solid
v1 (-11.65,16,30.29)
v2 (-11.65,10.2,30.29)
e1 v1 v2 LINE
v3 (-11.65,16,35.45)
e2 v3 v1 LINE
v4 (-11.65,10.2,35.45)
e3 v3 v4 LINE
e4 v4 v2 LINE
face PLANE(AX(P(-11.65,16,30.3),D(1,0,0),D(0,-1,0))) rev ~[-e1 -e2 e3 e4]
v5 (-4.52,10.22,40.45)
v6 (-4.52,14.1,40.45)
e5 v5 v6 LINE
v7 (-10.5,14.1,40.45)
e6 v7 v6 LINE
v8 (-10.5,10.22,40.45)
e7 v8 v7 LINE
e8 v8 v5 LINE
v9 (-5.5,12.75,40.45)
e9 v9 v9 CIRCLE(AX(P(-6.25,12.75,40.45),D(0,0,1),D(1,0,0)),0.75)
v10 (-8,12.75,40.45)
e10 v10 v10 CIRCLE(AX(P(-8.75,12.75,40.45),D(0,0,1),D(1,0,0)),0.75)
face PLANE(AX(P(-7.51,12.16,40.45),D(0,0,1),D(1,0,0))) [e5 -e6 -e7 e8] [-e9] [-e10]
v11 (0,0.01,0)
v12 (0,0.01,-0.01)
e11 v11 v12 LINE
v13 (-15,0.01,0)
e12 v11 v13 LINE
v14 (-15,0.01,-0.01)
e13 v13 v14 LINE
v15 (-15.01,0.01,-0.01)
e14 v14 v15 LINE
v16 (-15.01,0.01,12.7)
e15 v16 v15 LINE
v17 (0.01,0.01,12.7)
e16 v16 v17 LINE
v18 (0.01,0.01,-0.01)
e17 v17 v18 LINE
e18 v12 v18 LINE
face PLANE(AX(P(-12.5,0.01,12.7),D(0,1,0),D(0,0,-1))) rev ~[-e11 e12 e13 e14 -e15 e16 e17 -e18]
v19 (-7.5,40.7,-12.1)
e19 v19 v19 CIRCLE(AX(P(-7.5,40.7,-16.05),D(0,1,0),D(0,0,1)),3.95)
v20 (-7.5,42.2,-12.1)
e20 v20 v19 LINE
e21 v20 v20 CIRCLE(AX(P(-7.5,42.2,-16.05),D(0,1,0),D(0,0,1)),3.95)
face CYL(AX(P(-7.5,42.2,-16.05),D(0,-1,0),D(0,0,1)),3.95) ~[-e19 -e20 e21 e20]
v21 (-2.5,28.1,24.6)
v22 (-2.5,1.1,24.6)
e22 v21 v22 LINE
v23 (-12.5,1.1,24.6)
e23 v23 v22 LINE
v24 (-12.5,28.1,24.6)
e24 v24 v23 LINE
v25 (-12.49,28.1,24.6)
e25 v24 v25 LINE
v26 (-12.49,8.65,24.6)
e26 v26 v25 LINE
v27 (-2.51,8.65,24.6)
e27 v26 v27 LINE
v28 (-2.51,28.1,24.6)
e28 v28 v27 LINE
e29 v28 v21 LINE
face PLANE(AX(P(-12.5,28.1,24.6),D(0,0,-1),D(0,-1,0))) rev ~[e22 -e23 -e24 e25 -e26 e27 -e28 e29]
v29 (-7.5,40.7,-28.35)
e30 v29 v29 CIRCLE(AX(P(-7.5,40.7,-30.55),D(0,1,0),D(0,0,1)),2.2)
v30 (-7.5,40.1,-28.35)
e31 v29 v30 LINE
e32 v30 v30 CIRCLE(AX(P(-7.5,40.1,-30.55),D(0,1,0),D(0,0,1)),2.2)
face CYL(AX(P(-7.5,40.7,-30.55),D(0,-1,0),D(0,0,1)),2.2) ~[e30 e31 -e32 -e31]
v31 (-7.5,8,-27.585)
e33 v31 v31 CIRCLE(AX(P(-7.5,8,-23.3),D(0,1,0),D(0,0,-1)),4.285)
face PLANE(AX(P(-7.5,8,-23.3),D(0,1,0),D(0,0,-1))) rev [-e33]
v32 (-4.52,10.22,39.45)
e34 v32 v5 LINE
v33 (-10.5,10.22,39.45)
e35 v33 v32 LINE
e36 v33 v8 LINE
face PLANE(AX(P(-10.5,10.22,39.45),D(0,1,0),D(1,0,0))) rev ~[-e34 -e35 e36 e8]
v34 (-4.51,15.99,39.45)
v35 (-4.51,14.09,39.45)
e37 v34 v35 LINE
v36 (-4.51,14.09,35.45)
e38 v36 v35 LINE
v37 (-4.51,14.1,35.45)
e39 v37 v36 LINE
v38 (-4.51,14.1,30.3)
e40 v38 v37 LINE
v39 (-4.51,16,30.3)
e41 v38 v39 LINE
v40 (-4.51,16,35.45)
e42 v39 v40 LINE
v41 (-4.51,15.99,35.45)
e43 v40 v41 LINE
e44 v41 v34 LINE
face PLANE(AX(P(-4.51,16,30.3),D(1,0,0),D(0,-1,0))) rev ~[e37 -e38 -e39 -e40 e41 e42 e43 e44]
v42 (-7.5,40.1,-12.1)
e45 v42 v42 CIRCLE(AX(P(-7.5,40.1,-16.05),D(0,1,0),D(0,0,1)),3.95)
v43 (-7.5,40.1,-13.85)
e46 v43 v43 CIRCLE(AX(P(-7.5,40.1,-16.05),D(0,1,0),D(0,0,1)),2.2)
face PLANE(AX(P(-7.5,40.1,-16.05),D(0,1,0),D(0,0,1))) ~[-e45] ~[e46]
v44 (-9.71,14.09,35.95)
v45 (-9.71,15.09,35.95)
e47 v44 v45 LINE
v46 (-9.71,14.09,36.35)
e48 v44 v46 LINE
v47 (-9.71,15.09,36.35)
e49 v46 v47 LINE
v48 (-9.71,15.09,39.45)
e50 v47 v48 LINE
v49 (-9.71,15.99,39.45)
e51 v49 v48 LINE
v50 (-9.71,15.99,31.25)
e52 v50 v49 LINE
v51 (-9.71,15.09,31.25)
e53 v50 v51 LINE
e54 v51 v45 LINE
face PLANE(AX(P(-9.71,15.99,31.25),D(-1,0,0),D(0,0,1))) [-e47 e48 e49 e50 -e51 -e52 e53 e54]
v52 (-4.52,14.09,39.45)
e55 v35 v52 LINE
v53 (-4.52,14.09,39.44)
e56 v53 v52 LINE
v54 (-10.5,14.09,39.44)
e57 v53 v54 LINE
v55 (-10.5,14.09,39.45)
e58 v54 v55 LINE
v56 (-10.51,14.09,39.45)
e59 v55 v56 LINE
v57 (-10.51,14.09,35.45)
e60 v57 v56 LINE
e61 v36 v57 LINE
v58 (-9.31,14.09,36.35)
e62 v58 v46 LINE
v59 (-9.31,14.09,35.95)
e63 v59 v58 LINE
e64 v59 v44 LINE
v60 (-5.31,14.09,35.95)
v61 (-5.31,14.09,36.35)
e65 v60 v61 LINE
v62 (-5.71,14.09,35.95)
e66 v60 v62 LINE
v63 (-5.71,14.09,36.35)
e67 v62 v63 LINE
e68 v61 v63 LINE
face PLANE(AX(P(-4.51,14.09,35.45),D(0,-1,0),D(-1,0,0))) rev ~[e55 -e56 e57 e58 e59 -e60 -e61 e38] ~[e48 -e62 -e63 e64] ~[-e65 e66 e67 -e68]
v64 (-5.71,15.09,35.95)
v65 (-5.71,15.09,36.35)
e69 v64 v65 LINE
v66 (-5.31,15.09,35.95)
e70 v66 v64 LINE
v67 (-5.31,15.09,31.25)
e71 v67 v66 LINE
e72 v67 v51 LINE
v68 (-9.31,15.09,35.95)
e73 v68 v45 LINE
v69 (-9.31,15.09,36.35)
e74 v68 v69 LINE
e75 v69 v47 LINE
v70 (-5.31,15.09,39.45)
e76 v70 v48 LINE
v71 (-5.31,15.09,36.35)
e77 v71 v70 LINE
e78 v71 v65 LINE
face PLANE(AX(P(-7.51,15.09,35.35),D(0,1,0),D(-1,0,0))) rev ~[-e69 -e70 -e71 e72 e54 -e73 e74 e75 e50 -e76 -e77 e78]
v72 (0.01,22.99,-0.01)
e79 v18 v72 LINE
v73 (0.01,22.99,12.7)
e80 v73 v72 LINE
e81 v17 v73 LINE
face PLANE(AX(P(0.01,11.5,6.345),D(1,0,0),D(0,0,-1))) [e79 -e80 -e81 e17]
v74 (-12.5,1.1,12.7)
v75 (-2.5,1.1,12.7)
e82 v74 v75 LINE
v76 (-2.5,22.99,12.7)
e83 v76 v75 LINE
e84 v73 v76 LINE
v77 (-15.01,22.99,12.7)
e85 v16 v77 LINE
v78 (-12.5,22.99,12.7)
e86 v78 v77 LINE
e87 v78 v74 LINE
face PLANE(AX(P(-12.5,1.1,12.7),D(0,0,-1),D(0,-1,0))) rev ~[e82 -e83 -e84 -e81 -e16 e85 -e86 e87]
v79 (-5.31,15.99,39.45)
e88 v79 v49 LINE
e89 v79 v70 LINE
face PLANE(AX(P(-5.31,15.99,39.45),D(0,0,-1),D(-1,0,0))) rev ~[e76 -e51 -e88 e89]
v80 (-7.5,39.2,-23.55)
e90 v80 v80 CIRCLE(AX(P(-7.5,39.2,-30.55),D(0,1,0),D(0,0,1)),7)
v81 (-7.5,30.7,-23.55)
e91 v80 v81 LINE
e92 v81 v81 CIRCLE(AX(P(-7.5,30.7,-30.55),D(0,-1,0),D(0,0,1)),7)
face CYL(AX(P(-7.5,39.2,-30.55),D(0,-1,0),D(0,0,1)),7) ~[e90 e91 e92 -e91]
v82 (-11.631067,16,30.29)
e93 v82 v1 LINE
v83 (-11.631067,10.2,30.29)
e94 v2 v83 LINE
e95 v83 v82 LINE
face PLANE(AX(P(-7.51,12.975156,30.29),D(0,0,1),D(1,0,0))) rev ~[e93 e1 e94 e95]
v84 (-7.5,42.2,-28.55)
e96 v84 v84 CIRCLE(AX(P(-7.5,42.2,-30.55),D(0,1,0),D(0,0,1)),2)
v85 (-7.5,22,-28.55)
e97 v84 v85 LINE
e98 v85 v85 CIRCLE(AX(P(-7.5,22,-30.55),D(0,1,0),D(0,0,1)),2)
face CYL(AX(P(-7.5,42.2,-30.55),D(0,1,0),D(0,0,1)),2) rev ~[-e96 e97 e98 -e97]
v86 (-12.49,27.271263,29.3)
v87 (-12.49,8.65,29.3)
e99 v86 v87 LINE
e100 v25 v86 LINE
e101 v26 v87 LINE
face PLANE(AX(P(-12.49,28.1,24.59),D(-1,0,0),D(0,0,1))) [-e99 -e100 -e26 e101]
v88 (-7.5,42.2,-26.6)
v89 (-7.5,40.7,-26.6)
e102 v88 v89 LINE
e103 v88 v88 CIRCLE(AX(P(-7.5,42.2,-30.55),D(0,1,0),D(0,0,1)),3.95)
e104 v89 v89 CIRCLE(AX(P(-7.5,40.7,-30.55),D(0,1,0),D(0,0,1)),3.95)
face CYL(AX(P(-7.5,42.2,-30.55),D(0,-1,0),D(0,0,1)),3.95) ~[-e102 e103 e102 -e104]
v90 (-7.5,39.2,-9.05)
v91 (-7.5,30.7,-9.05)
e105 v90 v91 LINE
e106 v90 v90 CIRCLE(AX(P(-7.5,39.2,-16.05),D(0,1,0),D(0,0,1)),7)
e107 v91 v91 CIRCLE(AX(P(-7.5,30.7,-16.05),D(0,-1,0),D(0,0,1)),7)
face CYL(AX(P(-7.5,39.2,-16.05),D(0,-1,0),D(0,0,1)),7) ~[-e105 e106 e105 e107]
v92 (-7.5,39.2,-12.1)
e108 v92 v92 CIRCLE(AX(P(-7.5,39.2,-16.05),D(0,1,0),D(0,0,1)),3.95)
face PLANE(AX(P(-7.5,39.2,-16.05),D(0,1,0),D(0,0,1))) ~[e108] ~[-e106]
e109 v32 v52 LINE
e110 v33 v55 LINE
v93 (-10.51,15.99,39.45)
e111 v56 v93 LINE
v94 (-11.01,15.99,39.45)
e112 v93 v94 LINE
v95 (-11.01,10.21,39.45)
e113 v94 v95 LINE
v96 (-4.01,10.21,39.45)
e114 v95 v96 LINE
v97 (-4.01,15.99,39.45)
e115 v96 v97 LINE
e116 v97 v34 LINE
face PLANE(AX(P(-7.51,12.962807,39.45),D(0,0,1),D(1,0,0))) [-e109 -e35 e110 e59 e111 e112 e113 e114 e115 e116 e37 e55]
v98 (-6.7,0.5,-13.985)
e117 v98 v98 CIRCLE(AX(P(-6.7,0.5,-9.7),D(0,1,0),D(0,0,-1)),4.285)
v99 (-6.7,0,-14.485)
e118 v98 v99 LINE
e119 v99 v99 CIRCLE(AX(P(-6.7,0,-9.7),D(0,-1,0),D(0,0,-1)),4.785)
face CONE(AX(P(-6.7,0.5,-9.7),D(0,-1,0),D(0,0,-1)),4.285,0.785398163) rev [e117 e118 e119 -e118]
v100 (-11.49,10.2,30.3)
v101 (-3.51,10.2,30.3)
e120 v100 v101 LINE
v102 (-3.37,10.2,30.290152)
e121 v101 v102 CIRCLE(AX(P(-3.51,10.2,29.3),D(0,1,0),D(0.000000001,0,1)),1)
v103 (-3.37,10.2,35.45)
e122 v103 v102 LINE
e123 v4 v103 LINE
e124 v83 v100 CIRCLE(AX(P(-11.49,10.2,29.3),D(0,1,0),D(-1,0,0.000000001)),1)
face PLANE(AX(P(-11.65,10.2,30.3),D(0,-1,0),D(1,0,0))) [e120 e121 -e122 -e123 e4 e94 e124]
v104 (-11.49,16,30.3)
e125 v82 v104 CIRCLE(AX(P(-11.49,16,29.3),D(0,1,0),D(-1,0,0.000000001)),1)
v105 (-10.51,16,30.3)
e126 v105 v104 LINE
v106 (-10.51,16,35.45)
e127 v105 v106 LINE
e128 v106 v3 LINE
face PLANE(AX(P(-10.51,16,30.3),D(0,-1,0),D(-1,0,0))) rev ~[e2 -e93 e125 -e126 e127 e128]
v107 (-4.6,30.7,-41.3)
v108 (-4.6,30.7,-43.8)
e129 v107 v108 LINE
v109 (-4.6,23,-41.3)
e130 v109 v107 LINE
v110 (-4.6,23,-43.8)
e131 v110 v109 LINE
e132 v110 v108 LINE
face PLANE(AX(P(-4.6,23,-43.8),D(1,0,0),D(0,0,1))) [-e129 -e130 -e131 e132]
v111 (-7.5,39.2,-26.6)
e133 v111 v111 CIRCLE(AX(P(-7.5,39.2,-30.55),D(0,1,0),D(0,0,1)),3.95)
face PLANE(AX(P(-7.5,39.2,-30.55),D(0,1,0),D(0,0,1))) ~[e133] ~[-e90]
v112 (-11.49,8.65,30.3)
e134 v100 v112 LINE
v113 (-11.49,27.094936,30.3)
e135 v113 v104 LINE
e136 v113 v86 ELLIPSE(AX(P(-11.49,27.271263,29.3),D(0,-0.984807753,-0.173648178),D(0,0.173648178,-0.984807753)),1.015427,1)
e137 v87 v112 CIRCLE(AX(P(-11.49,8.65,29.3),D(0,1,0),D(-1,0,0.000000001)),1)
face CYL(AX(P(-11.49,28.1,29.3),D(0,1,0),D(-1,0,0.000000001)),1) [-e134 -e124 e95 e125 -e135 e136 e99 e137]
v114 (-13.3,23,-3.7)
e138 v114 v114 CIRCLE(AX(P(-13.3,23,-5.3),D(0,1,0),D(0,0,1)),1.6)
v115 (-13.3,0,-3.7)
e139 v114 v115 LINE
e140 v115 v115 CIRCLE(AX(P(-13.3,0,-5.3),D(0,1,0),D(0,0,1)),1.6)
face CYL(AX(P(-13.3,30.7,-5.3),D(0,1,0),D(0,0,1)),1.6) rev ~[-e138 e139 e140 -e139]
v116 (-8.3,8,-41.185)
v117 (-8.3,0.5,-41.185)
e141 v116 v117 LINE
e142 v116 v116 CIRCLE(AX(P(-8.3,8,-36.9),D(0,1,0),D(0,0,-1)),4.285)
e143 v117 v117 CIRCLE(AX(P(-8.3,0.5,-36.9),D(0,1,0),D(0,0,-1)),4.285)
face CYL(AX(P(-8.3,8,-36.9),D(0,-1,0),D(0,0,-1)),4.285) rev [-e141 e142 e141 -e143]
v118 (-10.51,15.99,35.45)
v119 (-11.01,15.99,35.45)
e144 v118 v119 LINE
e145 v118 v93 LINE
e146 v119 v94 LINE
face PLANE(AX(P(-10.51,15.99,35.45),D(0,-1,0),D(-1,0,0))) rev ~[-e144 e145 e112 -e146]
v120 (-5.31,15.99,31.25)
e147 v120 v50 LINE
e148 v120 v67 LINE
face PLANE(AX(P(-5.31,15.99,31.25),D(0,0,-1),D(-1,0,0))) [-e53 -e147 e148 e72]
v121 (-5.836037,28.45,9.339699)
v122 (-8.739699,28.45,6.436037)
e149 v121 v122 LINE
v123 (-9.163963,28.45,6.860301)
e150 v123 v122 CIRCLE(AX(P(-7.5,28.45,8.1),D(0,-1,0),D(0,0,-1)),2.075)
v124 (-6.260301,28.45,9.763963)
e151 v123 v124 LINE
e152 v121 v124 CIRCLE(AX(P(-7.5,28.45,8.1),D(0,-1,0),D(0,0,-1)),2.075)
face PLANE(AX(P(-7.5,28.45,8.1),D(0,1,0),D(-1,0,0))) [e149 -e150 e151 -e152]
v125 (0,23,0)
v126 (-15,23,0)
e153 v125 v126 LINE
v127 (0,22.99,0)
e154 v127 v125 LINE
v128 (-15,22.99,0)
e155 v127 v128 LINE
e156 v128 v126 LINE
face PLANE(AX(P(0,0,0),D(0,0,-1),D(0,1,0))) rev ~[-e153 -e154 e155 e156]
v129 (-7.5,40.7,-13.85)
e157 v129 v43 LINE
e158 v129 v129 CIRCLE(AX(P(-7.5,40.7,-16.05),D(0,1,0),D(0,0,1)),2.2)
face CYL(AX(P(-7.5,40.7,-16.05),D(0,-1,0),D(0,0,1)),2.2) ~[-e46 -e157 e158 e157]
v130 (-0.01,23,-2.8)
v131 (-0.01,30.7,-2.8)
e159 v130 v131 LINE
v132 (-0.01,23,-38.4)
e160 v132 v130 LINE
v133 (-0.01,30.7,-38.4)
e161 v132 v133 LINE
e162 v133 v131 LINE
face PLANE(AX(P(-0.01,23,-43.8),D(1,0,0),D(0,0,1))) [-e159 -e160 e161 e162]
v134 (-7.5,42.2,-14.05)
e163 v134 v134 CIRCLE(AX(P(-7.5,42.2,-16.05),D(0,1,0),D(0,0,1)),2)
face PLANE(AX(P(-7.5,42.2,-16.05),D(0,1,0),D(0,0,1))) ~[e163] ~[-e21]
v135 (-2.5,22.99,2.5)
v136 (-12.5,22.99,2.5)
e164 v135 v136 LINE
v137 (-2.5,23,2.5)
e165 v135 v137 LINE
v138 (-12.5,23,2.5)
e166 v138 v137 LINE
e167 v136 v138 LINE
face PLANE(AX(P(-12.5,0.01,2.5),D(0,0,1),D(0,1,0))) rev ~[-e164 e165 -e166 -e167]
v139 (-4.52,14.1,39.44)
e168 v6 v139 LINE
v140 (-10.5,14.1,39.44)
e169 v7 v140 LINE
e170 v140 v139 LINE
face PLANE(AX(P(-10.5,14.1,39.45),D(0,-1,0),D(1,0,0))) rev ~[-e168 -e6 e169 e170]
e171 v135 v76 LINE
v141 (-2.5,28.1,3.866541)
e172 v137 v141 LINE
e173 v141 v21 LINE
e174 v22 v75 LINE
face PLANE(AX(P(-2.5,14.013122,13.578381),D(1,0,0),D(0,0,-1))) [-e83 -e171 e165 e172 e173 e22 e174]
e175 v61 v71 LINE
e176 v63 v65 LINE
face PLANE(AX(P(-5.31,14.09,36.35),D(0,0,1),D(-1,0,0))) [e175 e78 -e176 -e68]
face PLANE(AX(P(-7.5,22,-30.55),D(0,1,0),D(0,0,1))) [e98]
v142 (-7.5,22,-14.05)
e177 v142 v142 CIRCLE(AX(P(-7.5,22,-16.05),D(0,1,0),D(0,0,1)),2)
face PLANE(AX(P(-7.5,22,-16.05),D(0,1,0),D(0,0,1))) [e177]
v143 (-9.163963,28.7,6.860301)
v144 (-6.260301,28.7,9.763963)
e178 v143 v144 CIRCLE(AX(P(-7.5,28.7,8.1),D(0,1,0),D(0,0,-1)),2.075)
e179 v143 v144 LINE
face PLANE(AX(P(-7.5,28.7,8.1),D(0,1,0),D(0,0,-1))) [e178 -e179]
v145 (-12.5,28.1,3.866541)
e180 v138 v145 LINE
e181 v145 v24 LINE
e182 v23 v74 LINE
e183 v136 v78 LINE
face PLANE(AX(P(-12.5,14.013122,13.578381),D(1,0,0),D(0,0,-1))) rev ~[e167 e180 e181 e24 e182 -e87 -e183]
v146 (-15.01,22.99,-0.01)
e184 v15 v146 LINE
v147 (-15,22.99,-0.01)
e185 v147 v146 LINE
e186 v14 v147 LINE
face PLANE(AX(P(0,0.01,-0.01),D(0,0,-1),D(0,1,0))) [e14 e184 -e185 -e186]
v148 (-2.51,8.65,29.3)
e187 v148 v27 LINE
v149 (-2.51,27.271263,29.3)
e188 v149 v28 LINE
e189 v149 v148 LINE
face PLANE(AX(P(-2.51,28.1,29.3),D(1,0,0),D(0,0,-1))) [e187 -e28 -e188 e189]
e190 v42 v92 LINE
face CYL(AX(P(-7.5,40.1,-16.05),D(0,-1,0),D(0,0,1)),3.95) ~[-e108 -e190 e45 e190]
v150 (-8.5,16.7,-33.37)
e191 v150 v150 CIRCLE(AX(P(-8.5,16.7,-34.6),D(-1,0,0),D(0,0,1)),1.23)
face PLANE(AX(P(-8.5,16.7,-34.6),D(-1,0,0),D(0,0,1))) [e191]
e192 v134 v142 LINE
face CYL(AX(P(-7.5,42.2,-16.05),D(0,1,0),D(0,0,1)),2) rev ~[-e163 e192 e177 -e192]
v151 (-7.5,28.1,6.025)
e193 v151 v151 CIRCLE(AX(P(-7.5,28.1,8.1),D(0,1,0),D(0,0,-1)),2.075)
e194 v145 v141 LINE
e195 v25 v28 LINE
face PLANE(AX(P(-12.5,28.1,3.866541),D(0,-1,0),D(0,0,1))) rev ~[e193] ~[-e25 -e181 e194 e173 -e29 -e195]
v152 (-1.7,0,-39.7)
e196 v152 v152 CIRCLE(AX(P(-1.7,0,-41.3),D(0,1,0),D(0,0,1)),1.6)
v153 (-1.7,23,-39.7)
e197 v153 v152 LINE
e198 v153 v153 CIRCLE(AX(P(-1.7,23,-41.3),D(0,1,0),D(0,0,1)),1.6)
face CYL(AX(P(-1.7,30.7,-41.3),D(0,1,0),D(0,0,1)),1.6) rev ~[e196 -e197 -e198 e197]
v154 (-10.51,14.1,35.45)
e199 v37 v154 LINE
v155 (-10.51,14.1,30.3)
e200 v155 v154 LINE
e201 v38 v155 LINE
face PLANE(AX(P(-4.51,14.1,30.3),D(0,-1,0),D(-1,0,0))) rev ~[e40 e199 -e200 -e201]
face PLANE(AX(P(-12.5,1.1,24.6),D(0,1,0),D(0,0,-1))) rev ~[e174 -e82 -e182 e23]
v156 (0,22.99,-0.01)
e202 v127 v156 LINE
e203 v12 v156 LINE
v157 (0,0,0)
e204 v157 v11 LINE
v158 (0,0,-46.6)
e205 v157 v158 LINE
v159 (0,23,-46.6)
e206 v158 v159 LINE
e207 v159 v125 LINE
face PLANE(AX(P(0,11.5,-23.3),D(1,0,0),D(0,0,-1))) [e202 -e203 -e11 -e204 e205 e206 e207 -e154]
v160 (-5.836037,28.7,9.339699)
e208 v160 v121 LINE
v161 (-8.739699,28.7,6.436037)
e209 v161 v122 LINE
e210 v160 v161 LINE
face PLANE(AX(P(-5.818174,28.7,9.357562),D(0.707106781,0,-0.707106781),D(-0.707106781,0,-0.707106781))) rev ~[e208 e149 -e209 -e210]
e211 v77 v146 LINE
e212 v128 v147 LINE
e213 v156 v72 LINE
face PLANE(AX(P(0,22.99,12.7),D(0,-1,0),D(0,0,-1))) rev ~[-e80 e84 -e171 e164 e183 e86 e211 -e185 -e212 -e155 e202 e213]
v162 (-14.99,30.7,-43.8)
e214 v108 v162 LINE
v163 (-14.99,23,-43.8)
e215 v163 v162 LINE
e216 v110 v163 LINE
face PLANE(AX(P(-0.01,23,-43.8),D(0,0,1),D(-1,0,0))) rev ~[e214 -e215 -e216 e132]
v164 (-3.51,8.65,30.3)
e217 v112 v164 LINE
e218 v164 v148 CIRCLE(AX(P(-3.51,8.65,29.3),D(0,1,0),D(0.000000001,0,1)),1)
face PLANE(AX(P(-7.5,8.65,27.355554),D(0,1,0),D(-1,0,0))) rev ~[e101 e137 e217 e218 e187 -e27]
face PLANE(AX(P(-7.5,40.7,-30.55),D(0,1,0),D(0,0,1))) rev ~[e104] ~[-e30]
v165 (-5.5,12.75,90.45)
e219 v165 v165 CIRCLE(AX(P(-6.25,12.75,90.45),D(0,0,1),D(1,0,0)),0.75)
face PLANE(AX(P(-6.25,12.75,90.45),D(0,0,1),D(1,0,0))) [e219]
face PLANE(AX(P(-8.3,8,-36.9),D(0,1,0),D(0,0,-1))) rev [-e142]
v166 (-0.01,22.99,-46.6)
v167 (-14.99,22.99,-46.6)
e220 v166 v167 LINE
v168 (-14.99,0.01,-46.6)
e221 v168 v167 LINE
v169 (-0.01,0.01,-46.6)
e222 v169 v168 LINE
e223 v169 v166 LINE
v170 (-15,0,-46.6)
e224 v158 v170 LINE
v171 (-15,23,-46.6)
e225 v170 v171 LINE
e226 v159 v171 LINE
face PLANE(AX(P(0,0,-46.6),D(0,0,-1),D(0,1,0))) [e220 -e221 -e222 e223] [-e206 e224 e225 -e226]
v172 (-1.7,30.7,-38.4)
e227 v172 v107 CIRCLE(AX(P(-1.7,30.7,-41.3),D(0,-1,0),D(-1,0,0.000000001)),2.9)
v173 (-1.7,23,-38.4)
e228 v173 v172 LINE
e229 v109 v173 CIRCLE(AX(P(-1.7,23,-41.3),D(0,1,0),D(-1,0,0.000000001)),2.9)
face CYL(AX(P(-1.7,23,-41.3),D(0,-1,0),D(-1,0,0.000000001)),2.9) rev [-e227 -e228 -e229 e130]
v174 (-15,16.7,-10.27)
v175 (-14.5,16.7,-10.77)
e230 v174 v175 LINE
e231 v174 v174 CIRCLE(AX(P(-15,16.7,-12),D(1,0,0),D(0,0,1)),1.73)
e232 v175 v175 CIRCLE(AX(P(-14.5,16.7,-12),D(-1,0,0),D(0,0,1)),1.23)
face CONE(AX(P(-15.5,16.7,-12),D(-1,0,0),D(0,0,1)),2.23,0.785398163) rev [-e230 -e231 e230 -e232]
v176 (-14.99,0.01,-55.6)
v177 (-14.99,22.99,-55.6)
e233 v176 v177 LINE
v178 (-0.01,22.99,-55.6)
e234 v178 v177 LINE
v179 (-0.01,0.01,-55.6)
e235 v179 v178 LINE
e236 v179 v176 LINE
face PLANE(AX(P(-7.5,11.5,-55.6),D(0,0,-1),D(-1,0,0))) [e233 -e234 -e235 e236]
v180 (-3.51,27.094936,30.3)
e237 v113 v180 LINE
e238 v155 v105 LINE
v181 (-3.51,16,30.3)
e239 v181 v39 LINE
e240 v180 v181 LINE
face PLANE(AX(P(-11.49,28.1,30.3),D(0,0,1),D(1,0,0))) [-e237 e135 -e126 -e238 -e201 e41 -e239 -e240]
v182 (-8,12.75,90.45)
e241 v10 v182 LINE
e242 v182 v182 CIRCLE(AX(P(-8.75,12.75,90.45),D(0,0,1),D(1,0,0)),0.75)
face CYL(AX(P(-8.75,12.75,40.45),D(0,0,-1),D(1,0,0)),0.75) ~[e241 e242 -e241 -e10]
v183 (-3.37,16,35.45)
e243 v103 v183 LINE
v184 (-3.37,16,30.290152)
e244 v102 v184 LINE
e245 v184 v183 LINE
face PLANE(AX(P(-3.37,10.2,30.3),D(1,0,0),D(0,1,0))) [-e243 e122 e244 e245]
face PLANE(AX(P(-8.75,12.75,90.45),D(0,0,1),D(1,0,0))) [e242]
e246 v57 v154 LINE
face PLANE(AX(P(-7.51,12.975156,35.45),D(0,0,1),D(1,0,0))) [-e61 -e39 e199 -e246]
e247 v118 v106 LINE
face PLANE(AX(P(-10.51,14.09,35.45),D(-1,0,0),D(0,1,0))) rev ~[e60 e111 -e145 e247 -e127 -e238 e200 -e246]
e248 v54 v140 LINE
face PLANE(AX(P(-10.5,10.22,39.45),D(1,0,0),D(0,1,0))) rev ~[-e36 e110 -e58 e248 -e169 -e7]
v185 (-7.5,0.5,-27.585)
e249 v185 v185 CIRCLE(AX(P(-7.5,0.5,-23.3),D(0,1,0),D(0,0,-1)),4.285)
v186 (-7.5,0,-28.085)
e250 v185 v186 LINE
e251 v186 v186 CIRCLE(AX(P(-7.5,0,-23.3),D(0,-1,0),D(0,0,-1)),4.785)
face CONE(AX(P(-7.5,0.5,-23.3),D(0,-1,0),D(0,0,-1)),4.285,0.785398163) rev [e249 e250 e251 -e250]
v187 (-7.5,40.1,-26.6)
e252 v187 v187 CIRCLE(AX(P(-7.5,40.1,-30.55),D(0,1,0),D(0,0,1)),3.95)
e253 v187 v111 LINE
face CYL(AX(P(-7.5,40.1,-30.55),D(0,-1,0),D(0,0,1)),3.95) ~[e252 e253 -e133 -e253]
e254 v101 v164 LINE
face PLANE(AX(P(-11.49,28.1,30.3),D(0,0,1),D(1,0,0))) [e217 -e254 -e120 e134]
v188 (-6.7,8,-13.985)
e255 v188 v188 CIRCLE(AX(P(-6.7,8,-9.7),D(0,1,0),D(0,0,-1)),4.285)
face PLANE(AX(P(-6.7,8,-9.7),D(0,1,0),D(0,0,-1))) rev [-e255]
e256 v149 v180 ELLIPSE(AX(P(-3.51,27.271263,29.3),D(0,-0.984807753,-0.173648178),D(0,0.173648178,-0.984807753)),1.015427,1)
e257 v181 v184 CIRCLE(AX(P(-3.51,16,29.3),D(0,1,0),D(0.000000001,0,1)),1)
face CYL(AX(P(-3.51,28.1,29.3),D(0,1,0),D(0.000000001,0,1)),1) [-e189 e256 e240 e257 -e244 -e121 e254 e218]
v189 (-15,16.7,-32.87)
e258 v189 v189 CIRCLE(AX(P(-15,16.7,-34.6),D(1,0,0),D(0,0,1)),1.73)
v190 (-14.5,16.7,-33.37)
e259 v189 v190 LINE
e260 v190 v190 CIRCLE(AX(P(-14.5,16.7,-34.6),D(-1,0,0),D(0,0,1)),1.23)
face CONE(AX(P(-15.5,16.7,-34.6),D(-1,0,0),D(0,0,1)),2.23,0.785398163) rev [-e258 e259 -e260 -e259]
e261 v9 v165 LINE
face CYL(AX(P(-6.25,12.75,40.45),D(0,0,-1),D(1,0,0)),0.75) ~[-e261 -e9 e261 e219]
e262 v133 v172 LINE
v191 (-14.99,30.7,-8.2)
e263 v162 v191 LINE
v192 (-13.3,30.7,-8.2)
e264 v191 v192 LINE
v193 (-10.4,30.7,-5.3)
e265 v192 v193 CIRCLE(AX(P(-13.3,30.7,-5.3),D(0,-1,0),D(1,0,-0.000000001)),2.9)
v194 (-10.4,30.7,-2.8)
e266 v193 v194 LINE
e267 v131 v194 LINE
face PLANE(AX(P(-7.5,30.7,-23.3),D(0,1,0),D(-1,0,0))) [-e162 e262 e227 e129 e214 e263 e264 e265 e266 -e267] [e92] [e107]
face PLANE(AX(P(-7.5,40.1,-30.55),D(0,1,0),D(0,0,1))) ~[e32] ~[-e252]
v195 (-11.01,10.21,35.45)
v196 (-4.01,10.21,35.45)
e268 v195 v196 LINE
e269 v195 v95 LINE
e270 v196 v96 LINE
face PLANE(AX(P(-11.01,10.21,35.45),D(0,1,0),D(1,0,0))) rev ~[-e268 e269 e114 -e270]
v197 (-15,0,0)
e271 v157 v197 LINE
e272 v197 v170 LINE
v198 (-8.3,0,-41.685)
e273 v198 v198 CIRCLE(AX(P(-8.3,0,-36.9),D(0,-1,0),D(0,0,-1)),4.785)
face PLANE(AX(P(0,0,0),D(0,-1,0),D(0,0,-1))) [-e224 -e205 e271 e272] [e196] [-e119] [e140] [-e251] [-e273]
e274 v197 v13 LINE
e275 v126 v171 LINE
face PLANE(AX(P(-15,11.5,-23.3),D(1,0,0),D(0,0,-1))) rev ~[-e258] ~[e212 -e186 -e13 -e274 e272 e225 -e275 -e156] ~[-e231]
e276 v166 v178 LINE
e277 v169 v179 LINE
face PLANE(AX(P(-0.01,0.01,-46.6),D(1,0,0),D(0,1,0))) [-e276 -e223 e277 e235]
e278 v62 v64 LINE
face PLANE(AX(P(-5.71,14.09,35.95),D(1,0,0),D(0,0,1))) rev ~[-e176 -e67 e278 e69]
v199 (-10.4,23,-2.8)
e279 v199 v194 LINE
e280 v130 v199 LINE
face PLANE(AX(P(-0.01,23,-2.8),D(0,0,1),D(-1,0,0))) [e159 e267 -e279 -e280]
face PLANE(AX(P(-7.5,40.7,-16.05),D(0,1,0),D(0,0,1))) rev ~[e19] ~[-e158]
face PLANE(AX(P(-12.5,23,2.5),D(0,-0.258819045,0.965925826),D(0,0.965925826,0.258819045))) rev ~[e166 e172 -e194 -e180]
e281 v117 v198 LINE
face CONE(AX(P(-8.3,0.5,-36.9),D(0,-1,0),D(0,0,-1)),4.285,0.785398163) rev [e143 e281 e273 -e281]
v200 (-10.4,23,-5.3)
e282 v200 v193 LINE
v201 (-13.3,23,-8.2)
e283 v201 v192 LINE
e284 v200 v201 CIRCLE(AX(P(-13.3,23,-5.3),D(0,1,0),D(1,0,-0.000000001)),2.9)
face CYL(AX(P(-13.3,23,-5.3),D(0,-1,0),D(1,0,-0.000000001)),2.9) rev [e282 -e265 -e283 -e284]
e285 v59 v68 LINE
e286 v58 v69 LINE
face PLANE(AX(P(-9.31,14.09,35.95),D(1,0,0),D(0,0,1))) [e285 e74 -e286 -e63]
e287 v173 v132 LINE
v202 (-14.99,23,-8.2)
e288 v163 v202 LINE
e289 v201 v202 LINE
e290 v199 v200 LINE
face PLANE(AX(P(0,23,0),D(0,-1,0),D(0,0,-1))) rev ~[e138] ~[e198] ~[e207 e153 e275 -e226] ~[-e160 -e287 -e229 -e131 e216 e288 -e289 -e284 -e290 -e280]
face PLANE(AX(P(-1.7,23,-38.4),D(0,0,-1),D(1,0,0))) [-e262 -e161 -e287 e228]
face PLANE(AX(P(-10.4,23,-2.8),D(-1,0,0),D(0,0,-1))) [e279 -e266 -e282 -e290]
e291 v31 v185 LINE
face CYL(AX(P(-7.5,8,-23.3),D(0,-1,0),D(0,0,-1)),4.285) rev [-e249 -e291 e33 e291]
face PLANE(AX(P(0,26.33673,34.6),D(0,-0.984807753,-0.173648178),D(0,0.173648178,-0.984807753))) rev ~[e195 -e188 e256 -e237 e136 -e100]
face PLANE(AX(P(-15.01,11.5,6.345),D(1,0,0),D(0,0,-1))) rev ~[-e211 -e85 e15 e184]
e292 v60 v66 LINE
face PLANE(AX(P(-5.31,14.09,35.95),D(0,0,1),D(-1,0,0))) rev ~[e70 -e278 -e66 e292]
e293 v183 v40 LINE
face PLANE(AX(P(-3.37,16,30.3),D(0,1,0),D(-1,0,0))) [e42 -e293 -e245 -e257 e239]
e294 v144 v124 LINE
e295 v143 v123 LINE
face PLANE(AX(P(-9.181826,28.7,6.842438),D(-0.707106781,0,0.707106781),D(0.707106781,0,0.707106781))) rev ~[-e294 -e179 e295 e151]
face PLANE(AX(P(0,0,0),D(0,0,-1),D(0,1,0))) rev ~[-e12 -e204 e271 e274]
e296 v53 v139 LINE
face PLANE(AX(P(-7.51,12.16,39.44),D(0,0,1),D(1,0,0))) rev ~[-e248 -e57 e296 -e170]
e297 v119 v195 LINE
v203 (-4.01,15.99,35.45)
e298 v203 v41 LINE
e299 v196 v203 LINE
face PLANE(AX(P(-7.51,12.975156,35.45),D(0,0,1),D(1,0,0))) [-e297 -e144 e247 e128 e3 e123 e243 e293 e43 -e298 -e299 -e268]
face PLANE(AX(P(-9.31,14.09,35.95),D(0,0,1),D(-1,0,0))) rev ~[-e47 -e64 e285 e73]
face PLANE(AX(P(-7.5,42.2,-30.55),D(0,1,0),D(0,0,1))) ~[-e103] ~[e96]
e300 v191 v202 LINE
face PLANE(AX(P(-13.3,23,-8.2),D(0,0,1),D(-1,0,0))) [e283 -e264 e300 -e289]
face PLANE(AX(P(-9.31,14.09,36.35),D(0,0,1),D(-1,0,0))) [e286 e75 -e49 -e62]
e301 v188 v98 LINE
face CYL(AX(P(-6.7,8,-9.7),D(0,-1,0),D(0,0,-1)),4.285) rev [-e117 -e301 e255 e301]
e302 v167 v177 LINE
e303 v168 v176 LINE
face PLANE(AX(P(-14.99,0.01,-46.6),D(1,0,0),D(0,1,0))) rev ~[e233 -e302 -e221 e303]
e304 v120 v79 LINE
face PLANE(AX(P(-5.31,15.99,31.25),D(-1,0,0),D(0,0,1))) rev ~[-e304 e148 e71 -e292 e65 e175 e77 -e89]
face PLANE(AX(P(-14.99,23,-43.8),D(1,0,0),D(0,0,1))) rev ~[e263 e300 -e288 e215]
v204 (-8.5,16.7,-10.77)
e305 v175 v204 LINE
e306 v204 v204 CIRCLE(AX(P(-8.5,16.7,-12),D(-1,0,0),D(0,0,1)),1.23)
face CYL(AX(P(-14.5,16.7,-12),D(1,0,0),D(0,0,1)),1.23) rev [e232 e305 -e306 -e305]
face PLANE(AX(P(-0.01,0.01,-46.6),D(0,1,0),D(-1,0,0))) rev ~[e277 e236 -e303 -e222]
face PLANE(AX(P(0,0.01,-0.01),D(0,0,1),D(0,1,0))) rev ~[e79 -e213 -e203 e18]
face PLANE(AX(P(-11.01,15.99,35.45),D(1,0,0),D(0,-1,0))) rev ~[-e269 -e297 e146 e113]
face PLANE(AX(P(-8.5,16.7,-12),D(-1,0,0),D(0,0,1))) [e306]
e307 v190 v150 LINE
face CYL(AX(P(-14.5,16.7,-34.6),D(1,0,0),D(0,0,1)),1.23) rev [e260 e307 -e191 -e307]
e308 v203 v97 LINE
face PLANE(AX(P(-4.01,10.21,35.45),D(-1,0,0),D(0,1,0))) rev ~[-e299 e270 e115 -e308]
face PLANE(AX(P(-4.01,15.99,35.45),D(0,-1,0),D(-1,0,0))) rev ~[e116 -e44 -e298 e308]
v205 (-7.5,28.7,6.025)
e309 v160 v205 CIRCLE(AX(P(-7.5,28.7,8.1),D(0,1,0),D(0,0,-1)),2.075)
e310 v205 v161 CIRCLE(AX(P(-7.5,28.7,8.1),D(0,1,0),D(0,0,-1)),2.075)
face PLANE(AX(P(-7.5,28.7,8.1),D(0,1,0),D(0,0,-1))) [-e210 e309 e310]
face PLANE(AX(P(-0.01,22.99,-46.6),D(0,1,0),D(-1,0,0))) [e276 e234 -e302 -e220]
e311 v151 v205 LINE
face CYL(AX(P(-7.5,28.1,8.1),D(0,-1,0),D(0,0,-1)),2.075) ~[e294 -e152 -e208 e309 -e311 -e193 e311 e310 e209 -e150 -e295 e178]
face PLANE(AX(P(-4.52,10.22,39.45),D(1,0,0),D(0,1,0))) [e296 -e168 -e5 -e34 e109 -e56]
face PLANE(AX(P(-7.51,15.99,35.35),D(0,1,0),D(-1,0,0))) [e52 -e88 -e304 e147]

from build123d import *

# Parameters (mm, degrees)
SKETCH_1_W           = 46.6
SKETCH_1_H           = 23
EXTRUDE_1_DEPTH      = 15
SKETCH_2_W           = 14.98
SKETCH_2_H           = 22.98
EXTRUDE_2_DEPTH      = 9
SKETCH_3_W           = 14.98
SKETCH_3_H           = 22.98
EXTRUDE_3_DEPTH      = 0.01
SKETCH_7_W           = 12.71
SKETCH_7_H           = 22.98
EXTRUDE_4_DEPTH      = 0.01
SKETCH_8_W           = 12.71
SKETCH_8_H           = 22.98
EXTRUDE_5_DEPTH      = 15.01
EXTRUDE_6_DEPTH      = 5
EXTRUDE_6_DEPTH_BACK = 5
EXTRUDE_7_DEPTH      = 19.45
CUT_EXTRUDE_1_DEPTH  = 15
SKETCH_12_W          = 6
SKETCH_12_H          = 2.26
EXTRUDE_8_DEPTH      = 5.15
SKETCH_13_W          = 6
SKETCH_13_H          = 2.26
EXTRUDE_9_DEPTH      = 0.01
EXTRUDE_10_DEPTH     = 4
EXTRUDE_11_DEPTH     = 6
SKETCH_16_W          = 0.4
SKETCH_16_H          = 0.4
EXTRUDE_12_DEPTH     = 1.5
SKETCH_17_W          = 0.4
SKETCH_17_H          = 0.4
EXTRUDE_13_DEPTH     = 0.01
SKETCH_18_W          = 0.4
SKETCH_18_H          = 0.4
EXTRUDE_14_DEPTH     = 1.5
SKETCH_19_W          = 0.4
SKETCH_19_H          = 0.4
EXTRUDE_15_DEPTH     = 0.01
SKETCH_20_W          = 4.4
SKETCH_20_H          = 8.2
EXTRUDE_16_DEPTH     = 0.9
SKETCH_21_W          = 5.98
SKETCH_21_H          = 3.88
EXTRUDE_17_DEPTH     = 1
SKETCH_22_W          = 5.98
SKETCH_22_H          = 3.88
EXTRUDE_18_DEPTH     = 0.01
SKETCH_23_R          = 0.75
EXTRUDE_19_DEPTH     = 50
EXTRUDE_START        = -0.01
SKETCH_24_R          = 0.75
EXTRUDE_20_DEPTH     = 0.01
SKETCH_25_R          = 0.75
EXTRUDE_21_DEPTH     = 50
SKETCH_26_R          = 0.75
EXTRUDE_22_DEPTH     = 0.01
SKETCH_27_R          = 2.075
EXTRUDE_23_DEPTH     = 0.6
SKETCH_28_R          = 2.075
EXTRUDE_24_DEPTH     = 0.01
CUT_EXTRUDE_3_DEPTH  = 0.25
SKETCH_31_W          = 14.98
SKETCH_31_H          = 41
EXTRUDE_25_DEPTH     = 7.7
SKETCH_32_W          = 14.98
SKETCH_32_H          = 41
EXTRUDE_26_DEPTH     = 0.01
CUT_EXTRUDE_4_DEPTH  = 8.7
CUT_EXTRUDE_5_DEPTH  = 8.7
SKETCH_37_R          = 2
CUT_EXTRUDE_6_DEPTH  = 20.2
SKETCH_38_R          = 2
CUT_EXTRUDE_7_DEPTH  = 20.2
SKETCH_41_R          = 1.6
CUT_EXTRUDE_8_DEPTH  = 523


with BuildPart() as part:
    # 草图1 → 拉伸1 (new body)
    with BuildSketch(Plane(origin=(0, 0, 0), x_dir=(0, 0, -1), z_dir=(1, 0, 0))):
        with Locations((23.3, 11.5)):
            Rectangle(SKETCH_1_W, SKETCH_1_H)
    extrude(amount=-EXTRUDE_1_DEPTH)

    # 草图2 → 拉伸2 (add)
    with BuildSketch(Plane(origin=(0, 0, -46.6), x_dir=(-1, 0, 0), z_dir=(0, 0, -1))):
        with Locations((7.5, 11.5)):
            Rectangle(SKETCH_2_W, SKETCH_2_H)
    extrude(amount=EXTRUDE_2_DEPTH)

    # 草图3 → 拉伸3 (add)
    with BuildSketch(Plane(origin=(0, 0, -46.6), x_dir=(-1, 0, 0), z_dir=(0, 0, -1))):
        with Locations((7.5, 11.5)):
            Rectangle(SKETCH_3_W, SKETCH_3_H)
    extrude(amount=-EXTRUDE_3_DEPTH)

    # 草图4 → 切除-旋转1 (revolve, cut)
    with BuildSketch(Plane(origin=(-7.5, 0, 0), x_dir=(0, 0, -1), z_dir=(1, 0, 0))):
        Polygon((23.3, 8), (27.585, 8), (27.585, 0.5), (28.585, -0.5), (23.3, -0.5), align=None)
    revolve(axis=Axis((-7.5, -0.5, -23.3), (0, 1, 0)), mode=Mode.SUBTRACT)

    # 草图5 → 切除-旋转2 (revolve, cut)
    with BuildSketch(Plane(origin=(-6.7, 0, 0), x_dir=(0, 0, -1), z_dir=(1, 0, 0))):
        Polygon((9.7, 8), (13.985, 8), (13.985, 0.5), (14.985, -0.5), (9.7, -0.5), align=None)
    revolve(axis=Axis((-6.7, -0.5, -9.7), (0, 1, 0)), mode=Mode.SUBTRACT)

    # 草图6 → 切除-旋转3 (revolve, cut)
    with BuildSketch(Plane(origin=(-8.3, 0, 0), x_dir=(0, 0, -1), z_dir=(1, 0, 0))):
        Polygon((36.9, 8), (41.185, 8), (41.185, 0.5), (42.185, -0.5), (36.9, -0.5), align=None)
    revolve(axis=Axis((-8.3, -0.5, -36.9), (0, 1, 0)), mode=Mode.SUBTRACT)

    # 草图7 → 拉伸4 (add)
    with BuildSketch(Plane(origin=(0, 0, 0), x_dir=(0, 0, -1), z_dir=(1, 0, 0))):
        with Locations((-6.345, 11.5)):
            Rectangle(SKETCH_7_W, SKETCH_7_H)
    extrude(amount=EXTRUDE_4_DEPTH)

    # 草图8 → 拉伸5 (add)
    with BuildSketch(Plane(origin=(0, 0, 0), x_dir=(0, 0, -1), z_dir=(1, 0, 0))):
        with Locations((-6.345, 11.5)):
            Rectangle(SKETCH_8_W, SKETCH_8_H)
    extrude(amount=-EXTRUDE_5_DEPTH)

    # 草图9 → 拉伸6 (add, two sides: drawn at the far end of the back side and taken through both)
    with BuildSketch(Plane(origin=(-7.5, 0, 0), x_dir=(0, 0, -1), z_dir=(1, 0, 0)).offset(-EXTRUDE_6_DEPTH_BACK)):
        Polygon((-24.6, 1.1), (-12.7, 1.1), (-12.7, 0.01), (-2.5, 0.01), (-2.5, 23), (-3.866540881, 28.1), (-24.6, 28.1), align=None)
    extrude(amount=EXTRUDE_6_DEPTH + EXTRUDE_6_DEPTH_BACK)

    # 草图10 → 拉伸7 (add)
    with BuildSketch(Plane(origin=(0, 28.1, 0), x_dir=(-1, 0, 0), z_dir=(0, 1, 0))):
        with BuildLine():
            Line((12.49, 24.59), (12.49, 29.3))
            ThreePointArc((12.49, 29.3), (12.197106781, 30.007106781), (11.49, 30.3))
            Line((11.49, 30.3), (3.51, 30.3))
            ThreePointArc((3.51, 30.3), (2.802893219, 30.007106781), (2.51, 29.3))
            Line((2.51, 29.3), (2.51, 24.59))
            Line((2.51, 24.59), (12.49, 24.59))
        make_face()
    extrude(amount=-EXTRUDE_7_DEPTH)

    # 草图11 → 切除-拉伸1 (cut)
    with BuildSketch(Plane(origin=(0, 0, 0), x_dir=(0, 0, -1), z_dir=(1, 0, 0))):
        Polygon((-34.6, 26.336730193), (-13.257436361, 30.1), (-34.6, 30.1), align=None)
    extrude(amount=-CUT_EXTRUDE_1_DEPTH, mode=Mode.SUBTRACT)

    # 草图12 → 拉伸8 (add)
    with BuildSketch(Plane.XY.offset(30.3)):
        Polygon((-3.37, 10.2), (-3.37, 16), (-4.51, 16), (-4.51, 14.1), (-10.51, 14.1), (-10.51, 16), (-11.65, 16), (-11.65, 10.2), align=None)
        with Locations((-7.51, 12.47)):
            Rectangle(SKETCH_12_W, SKETCH_12_H, mode=Mode.SUBTRACT)
    extrude(amount=EXTRUDE_8_DEPTH)

    # 草图13 → 拉伸9 (add)
    with BuildSketch(Plane.XY.offset(30.3)):
        Polygon((-3.37, 10.2), (-3.37, 16), (-4.51, 16), (-4.51, 14.1), (-10.51, 14.1), (-10.51, 16), (-11.65, 16), (-11.65, 10.2), align=None)
        with Locations((-7.51, 12.47)):
            Rectangle(SKETCH_13_W, SKETCH_13_H, mode=Mode.SUBTRACT)
    extrude(amount=-EXTRUDE_9_DEPTH)

    # 草图14 → 拉伸10 (add)
    with BuildSketch(Plane.XY.offset(35.45)):
        Polygon((-11.01, 15.99), (-11.01, 10.21), (-4.01, 10.21), (-4.01, 15.99), (-4.51, 15.99), (-4.51, 14.09), (-10.51, 14.09), (-10.51, 15.99), align=None)
    extrude(amount=EXTRUDE_10_DEPTH)

    # 草图15 → 拉伸11 (add)
    with BuildSketch(Plane.XY.offset(35.45)):
        Polygon((-11.01, 15.99), (-11.01, 10.21), (-4.01, 10.21), (-4.01, 15.99), (-4.51, 15.99), (-4.51, 14.09), (-10.51, 14.09), (-10.51, 15.99), align=None)
    extrude(amount=-EXTRUDE_11_DEPTH)

    # 草图16 → 拉伸12 (add)
    with BuildSketch(Plane(origin=(0, 14.09, 0), x_dir=(-1, 0, 0), z_dir=(0, 1, 0))):
        with Locations((5.51, 36.15)):
            Rectangle(SKETCH_16_W, SKETCH_16_H)
    extrude(amount=EXTRUDE_12_DEPTH)

    # 草图17 → 拉伸13 (add)
    with BuildSketch(Plane(origin=(0, 14.09, 0), x_dir=(-1, 0, 0), z_dir=(0, 1, 0))):
        with Locations((5.51, 36.15)):
            Rectangle(SKETCH_17_W, SKETCH_17_H)
    extrude(amount=-EXTRUDE_13_DEPTH)

    # 草图18 → 拉伸14 (add)
    with BuildSketch(Plane(origin=(0, 14.09, 0), x_dir=(-1, 0, 0), z_dir=(0, 1, 0))):
        with Locations((9.51, 36.15)):
            Rectangle(SKETCH_18_W, SKETCH_18_H)
    extrude(amount=EXTRUDE_14_DEPTH)

    # 草图19 → 拉伸15 (add)
    with BuildSketch(Plane(origin=(0, 14.09, 0), x_dir=(-1, 0, 0), z_dir=(0, 1, 0))):
        with Locations((9.51, 36.15)):
            Rectangle(SKETCH_19_W, SKETCH_19_H)
    extrude(amount=-EXTRUDE_15_DEPTH)

    # 草图20 → 拉伸16 (add)
    with BuildSketch(Plane(origin=(0, 15.99, 0), x_dir=(-1, 0, 0), z_dir=(0, 1, 0))):
        with Locations((7.51, 35.35)):
            Rectangle(SKETCH_20_W, SKETCH_20_H)
    extrude(amount=-EXTRUDE_16_DEPTH)

    # 草图21 → 拉伸17 (add)
    with BuildSketch(Plane.XY.offset(39.45)):
        with Locations((-7.51, 12.16)):
            Rectangle(SKETCH_21_W, SKETCH_21_H)
    extrude(amount=EXTRUDE_17_DEPTH)

    # 草图22 → 拉伸18 (add)
    with BuildSketch(Plane.XY.offset(39.45)):
        with Locations((-7.51, 12.16)):
            Rectangle(SKETCH_22_W, SKETCH_22_H)
    extrude(amount=-EXTRUDE_18_DEPTH)

    # 草图23 → 拉伸19 (add)
    with BuildSketch(Plane.XY.offset(40.45)):
        with Locations((-8.75, 12.75)):
            Circle(SKETCH_23_R)
    extrude(amount=EXTRUDE_19_DEPTH)

    # 草图24 → 拉伸20 (add)
    with BuildSketch(Plane.XY.offset(40.45).offset(EXTRUDE_START)):
        with Locations((-8.75, 12.75)):
            Circle(SKETCH_24_R)
    extrude(amount=EXTRUDE_20_DEPTH)

    # 草图25 → 拉伸21 (add)
    with BuildSketch(Plane.XY.offset(40.45)):
        with Locations((-6.25, 12.75)):
            Circle(SKETCH_25_R)
    extrude(amount=EXTRUDE_21_DEPTH)

    # 草图26 → 拉伸22 (add)
    with BuildSketch(Plane.XY.offset(40.45).offset(EXTRUDE_START)):
        with Locations((-6.25, 12.75)):
            Circle(SKETCH_26_R)
    extrude(amount=EXTRUDE_22_DEPTH)

    # 草图27 → 拉伸23 (add)
    with BuildSketch(Plane(origin=(0, 28.1, 0), x_dir=(-1, 0, 0), z_dir=(0, 1, 0))):
        with Locations(Location((7.5, 8.1, 0), (0, 0, 270))):
            Circle(SKETCH_27_R)
    extrude(amount=EXTRUDE_23_DEPTH)

    # 草图28 → 拉伸24 (add)
    with BuildSketch(Plane(origin=(0, 28.1, 0), x_dir=(-1, 0, 0), z_dir=(0, 1, 0)).offset(EXTRUDE_START)):
        with Locations(Location((7.5, 8.1, 0), (0, 0, 270))):
            Circle(SKETCH_28_R)
    extrude(amount=EXTRUDE_24_DEPTH)

    # 草图30 → 切除-拉伸3 (cut)
    with BuildSketch(Plane(origin=(0, 28.7, 0), x_dir=(-1, 0, 0), z_dir=(0, 1, 0))):
        with BuildLine():
            Line((5.81817412, 9.357561811), (8.757561811, 6.41817412))
            ThreePointArc((8.757561811, 6.41817412), (8.98492424, 6.61507576), (9.18182588, 6.842438189))
            Line((9.18182588, 6.842438189), (6.242438189, 9.78182588))
            ThreePointArc((6.242438189, 9.78182588), (6.01507576, 9.58492424), (5.81817412, 9.357561811))
        make_face()
    extrude(amount=-CUT_EXTRUDE_3_DEPTH, mode=Mode.SUBTRACT)

    # 草图31 → 拉伸25 (add)
    with BuildSketch(Plane(origin=(0, 23, 0), x_dir=(-1, 0, 0), z_dir=(0, 1, 0))):
        with Locations((7.5, -23.3)):
            Rectangle(SKETCH_31_W, SKETCH_31_H)
    extrude(amount=EXTRUDE_25_DEPTH)

    # 草图32 → 拉伸26 (add)
    with BuildSketch(Plane(origin=(0, 23, 0), x_dir=(-1, 0, 0), z_dir=(0, 1, 0))):
        with Locations((7.5, -23.3)):
            Rectangle(SKETCH_32_W, SKETCH_32_H)
    extrude(amount=-EXTRUDE_26_DEPTH)

    # 草图33 → 切除-拉伸4 (cut)
    with BuildSketch(Plane(origin=(0, 23, 0), x_dir=(-1, 0, 0), z_dir=(0, 1, 0))):
        with BuildLine():
            Line((4.6, -43.8), (4.6, -41.3))
            ThreePointArc((4.6, -41.3), (3.750609665, -39.249390335), (1.7, -38.4))
            Line((1.7, -38.4), (-2, -38.4))
            Line((-2, -38.4), (-2, -43.8))
            Line((-2, -43.8), (4.6, -43.8))
        make_face()
    extrude(amount=CUT_EXTRUDE_4_DEPTH, mode=Mode.SUBTRACT)

    # 草图34 → 切除-拉伸5 (cut)
    with BuildSketch(Plane(origin=(0, 23, 0), x_dir=(-1, 0, 0), z_dir=(0, 1, 0))):
        with BuildLine():
            Line((16, -2.8), (10.4, -2.8))
            Line((10.4, -2.8), (10.4, -5.3))
            ThreePointArc((10.4, -5.3), (11.249390335, -7.350609665), (13.3, -8.2))
            Line((13.3, -8.2), (16, -8.2))
            Line((16, -8.2), (16, -2.8))
        make_face()
    extrude(amount=CUT_EXTRUDE_5_DEPTH, mode=Mode.SUBTRACT)

    # 草图35 → 旋转1 (revolve)
    with BuildSketch(Plane(origin=(-7.5, 0, 0), x_dir=(0, 0, -1), z_dir=(1, 0, 0)), mode=Mode.PRIVATE) as revolve_1_sk:
        Polygon((16.05, 42.2), (20, 42.2), (20, 40.7), (18.25, 40.7), (18.25, 40.1), (20, 40.1), (20, 39.2), (23.05, 39.2), (23.05, 30.69), (16.05, 30.69), align=None)
    revolve(revolve_1_sk.sketch.rotate(Axis((-7.5, 30.69, -16.05), (0, 1, 0)), 180), axis=Axis((-7.5, 30.69, -16.05), (0, 1, 0)))

    # 草图36 → 旋转2 (revolve)
    with BuildSketch(Plane(origin=(-7.5, 0, 0), x_dir=(0, 0, -1), z_dir=(1, 0, 0)), mode=Mode.PRIVATE) as revolve_2_sk:
        Polygon((30.55, 42.2), (34.5, 42.2), (34.5, 40.7), (32.75, 40.7), (32.75, 40.1), (34.5, 40.1), (34.5, 39.2), (37.55, 39.2), (37.55, 30.69), (30.55, 30.69), align=None)
    revolve(revolve_2_sk.sketch.rotate(Axis((-7.5, 30.69, -30.55), (0, 1, 0)), 180), axis=Axis((-7.5, 30.69, -30.55), (0, 1, 0)))

    # 草图37 → 切除-拉伸6 (cut)
    with BuildSketch(Plane(origin=(0, 42.2, 0), x_dir=(-1, 0, 0), z_dir=(0, 1, 0))):
        with Locations(Location((7.5, -16.05, 0), (0, 0, 90))):
            Circle(SKETCH_37_R)
    extrude(amount=-CUT_EXTRUDE_6_DEPTH, mode=Mode.SUBTRACT)

    # 草图38 → 切除-拉伸7 (cut)
    with BuildSketch(Plane(origin=(0, 42.2, 0), x_dir=(-1, 0, 0), z_dir=(0, 1, 0))):
        with Locations(Location((7.5, -30.55, 0), (0, 0, 90))):
            Circle(SKETCH_38_R)
    extrude(amount=-CUT_EXTRUDE_7_DEPTH, mode=Mode.SUBTRACT)

    # 草图39 → 切除-旋转4 (revolve, cut)
    with BuildSketch(Plane(origin=(0, 16.7, 0), x_dir=(-1, 0, 0), z_dir=(0, 1, 0)), mode=Mode.PRIVATE) as cut_revolve_4_sk:
        Polygon((15.5, -34.6), (15.5, -36.83), (14.5, -35.83), (8.5, -35.83), (8.5, -34.6), align=None)
    revolve(cut_revolve_4_sk.sketch.rotate(Axis((-8.5, 16.7, -34.6), (-1, 0, 0)), 180), axis=Axis((-8.5, 16.7, -34.6), (-1, 0, 0)), mode=Mode.SUBTRACT)

    # 草图40 → 切除-旋转5 (revolve, cut)
    with BuildSketch(Plane(origin=(0, 16.7, 0), x_dir=(-1, 0, 0), z_dir=(0, 1, 0)), mode=Mode.PRIVATE) as cut_revolve_5_sk:
        Polygon((15.5, -12), (15.5, -14.23), (14.5, -13.23), (8.5, -13.23), (8.5, -12), align=None)
    revolve(cut_revolve_5_sk.sketch.rotate(Axis((-8.5, 16.7, -12), (-1, 0, 0)), 180), axis=Axis((-8.5, 16.7, -12), (-1, 0, 0)), mode=Mode.SUBTRACT)

    # 草图41 → 切除-拉伸8 (cut)
    with BuildSketch(Plane(origin=(0, 30.7, 0), x_dir=(1, 0, 0), z_dir=(0, 1, 0))):
        with Locations(Location((-13.3, 5.3, 0), (0, 0, 270))):
            Circle(SKETCH_41_R)
        with Locations(Location((-1.7, 41.3, 0), (0, 0, 270))):
            Circle(SKETCH_41_R)
    extrude(amount=-CUT_EXTRUDE_8_DEPTH, mode=Mode.SUBTRACT)


solid = part.part
